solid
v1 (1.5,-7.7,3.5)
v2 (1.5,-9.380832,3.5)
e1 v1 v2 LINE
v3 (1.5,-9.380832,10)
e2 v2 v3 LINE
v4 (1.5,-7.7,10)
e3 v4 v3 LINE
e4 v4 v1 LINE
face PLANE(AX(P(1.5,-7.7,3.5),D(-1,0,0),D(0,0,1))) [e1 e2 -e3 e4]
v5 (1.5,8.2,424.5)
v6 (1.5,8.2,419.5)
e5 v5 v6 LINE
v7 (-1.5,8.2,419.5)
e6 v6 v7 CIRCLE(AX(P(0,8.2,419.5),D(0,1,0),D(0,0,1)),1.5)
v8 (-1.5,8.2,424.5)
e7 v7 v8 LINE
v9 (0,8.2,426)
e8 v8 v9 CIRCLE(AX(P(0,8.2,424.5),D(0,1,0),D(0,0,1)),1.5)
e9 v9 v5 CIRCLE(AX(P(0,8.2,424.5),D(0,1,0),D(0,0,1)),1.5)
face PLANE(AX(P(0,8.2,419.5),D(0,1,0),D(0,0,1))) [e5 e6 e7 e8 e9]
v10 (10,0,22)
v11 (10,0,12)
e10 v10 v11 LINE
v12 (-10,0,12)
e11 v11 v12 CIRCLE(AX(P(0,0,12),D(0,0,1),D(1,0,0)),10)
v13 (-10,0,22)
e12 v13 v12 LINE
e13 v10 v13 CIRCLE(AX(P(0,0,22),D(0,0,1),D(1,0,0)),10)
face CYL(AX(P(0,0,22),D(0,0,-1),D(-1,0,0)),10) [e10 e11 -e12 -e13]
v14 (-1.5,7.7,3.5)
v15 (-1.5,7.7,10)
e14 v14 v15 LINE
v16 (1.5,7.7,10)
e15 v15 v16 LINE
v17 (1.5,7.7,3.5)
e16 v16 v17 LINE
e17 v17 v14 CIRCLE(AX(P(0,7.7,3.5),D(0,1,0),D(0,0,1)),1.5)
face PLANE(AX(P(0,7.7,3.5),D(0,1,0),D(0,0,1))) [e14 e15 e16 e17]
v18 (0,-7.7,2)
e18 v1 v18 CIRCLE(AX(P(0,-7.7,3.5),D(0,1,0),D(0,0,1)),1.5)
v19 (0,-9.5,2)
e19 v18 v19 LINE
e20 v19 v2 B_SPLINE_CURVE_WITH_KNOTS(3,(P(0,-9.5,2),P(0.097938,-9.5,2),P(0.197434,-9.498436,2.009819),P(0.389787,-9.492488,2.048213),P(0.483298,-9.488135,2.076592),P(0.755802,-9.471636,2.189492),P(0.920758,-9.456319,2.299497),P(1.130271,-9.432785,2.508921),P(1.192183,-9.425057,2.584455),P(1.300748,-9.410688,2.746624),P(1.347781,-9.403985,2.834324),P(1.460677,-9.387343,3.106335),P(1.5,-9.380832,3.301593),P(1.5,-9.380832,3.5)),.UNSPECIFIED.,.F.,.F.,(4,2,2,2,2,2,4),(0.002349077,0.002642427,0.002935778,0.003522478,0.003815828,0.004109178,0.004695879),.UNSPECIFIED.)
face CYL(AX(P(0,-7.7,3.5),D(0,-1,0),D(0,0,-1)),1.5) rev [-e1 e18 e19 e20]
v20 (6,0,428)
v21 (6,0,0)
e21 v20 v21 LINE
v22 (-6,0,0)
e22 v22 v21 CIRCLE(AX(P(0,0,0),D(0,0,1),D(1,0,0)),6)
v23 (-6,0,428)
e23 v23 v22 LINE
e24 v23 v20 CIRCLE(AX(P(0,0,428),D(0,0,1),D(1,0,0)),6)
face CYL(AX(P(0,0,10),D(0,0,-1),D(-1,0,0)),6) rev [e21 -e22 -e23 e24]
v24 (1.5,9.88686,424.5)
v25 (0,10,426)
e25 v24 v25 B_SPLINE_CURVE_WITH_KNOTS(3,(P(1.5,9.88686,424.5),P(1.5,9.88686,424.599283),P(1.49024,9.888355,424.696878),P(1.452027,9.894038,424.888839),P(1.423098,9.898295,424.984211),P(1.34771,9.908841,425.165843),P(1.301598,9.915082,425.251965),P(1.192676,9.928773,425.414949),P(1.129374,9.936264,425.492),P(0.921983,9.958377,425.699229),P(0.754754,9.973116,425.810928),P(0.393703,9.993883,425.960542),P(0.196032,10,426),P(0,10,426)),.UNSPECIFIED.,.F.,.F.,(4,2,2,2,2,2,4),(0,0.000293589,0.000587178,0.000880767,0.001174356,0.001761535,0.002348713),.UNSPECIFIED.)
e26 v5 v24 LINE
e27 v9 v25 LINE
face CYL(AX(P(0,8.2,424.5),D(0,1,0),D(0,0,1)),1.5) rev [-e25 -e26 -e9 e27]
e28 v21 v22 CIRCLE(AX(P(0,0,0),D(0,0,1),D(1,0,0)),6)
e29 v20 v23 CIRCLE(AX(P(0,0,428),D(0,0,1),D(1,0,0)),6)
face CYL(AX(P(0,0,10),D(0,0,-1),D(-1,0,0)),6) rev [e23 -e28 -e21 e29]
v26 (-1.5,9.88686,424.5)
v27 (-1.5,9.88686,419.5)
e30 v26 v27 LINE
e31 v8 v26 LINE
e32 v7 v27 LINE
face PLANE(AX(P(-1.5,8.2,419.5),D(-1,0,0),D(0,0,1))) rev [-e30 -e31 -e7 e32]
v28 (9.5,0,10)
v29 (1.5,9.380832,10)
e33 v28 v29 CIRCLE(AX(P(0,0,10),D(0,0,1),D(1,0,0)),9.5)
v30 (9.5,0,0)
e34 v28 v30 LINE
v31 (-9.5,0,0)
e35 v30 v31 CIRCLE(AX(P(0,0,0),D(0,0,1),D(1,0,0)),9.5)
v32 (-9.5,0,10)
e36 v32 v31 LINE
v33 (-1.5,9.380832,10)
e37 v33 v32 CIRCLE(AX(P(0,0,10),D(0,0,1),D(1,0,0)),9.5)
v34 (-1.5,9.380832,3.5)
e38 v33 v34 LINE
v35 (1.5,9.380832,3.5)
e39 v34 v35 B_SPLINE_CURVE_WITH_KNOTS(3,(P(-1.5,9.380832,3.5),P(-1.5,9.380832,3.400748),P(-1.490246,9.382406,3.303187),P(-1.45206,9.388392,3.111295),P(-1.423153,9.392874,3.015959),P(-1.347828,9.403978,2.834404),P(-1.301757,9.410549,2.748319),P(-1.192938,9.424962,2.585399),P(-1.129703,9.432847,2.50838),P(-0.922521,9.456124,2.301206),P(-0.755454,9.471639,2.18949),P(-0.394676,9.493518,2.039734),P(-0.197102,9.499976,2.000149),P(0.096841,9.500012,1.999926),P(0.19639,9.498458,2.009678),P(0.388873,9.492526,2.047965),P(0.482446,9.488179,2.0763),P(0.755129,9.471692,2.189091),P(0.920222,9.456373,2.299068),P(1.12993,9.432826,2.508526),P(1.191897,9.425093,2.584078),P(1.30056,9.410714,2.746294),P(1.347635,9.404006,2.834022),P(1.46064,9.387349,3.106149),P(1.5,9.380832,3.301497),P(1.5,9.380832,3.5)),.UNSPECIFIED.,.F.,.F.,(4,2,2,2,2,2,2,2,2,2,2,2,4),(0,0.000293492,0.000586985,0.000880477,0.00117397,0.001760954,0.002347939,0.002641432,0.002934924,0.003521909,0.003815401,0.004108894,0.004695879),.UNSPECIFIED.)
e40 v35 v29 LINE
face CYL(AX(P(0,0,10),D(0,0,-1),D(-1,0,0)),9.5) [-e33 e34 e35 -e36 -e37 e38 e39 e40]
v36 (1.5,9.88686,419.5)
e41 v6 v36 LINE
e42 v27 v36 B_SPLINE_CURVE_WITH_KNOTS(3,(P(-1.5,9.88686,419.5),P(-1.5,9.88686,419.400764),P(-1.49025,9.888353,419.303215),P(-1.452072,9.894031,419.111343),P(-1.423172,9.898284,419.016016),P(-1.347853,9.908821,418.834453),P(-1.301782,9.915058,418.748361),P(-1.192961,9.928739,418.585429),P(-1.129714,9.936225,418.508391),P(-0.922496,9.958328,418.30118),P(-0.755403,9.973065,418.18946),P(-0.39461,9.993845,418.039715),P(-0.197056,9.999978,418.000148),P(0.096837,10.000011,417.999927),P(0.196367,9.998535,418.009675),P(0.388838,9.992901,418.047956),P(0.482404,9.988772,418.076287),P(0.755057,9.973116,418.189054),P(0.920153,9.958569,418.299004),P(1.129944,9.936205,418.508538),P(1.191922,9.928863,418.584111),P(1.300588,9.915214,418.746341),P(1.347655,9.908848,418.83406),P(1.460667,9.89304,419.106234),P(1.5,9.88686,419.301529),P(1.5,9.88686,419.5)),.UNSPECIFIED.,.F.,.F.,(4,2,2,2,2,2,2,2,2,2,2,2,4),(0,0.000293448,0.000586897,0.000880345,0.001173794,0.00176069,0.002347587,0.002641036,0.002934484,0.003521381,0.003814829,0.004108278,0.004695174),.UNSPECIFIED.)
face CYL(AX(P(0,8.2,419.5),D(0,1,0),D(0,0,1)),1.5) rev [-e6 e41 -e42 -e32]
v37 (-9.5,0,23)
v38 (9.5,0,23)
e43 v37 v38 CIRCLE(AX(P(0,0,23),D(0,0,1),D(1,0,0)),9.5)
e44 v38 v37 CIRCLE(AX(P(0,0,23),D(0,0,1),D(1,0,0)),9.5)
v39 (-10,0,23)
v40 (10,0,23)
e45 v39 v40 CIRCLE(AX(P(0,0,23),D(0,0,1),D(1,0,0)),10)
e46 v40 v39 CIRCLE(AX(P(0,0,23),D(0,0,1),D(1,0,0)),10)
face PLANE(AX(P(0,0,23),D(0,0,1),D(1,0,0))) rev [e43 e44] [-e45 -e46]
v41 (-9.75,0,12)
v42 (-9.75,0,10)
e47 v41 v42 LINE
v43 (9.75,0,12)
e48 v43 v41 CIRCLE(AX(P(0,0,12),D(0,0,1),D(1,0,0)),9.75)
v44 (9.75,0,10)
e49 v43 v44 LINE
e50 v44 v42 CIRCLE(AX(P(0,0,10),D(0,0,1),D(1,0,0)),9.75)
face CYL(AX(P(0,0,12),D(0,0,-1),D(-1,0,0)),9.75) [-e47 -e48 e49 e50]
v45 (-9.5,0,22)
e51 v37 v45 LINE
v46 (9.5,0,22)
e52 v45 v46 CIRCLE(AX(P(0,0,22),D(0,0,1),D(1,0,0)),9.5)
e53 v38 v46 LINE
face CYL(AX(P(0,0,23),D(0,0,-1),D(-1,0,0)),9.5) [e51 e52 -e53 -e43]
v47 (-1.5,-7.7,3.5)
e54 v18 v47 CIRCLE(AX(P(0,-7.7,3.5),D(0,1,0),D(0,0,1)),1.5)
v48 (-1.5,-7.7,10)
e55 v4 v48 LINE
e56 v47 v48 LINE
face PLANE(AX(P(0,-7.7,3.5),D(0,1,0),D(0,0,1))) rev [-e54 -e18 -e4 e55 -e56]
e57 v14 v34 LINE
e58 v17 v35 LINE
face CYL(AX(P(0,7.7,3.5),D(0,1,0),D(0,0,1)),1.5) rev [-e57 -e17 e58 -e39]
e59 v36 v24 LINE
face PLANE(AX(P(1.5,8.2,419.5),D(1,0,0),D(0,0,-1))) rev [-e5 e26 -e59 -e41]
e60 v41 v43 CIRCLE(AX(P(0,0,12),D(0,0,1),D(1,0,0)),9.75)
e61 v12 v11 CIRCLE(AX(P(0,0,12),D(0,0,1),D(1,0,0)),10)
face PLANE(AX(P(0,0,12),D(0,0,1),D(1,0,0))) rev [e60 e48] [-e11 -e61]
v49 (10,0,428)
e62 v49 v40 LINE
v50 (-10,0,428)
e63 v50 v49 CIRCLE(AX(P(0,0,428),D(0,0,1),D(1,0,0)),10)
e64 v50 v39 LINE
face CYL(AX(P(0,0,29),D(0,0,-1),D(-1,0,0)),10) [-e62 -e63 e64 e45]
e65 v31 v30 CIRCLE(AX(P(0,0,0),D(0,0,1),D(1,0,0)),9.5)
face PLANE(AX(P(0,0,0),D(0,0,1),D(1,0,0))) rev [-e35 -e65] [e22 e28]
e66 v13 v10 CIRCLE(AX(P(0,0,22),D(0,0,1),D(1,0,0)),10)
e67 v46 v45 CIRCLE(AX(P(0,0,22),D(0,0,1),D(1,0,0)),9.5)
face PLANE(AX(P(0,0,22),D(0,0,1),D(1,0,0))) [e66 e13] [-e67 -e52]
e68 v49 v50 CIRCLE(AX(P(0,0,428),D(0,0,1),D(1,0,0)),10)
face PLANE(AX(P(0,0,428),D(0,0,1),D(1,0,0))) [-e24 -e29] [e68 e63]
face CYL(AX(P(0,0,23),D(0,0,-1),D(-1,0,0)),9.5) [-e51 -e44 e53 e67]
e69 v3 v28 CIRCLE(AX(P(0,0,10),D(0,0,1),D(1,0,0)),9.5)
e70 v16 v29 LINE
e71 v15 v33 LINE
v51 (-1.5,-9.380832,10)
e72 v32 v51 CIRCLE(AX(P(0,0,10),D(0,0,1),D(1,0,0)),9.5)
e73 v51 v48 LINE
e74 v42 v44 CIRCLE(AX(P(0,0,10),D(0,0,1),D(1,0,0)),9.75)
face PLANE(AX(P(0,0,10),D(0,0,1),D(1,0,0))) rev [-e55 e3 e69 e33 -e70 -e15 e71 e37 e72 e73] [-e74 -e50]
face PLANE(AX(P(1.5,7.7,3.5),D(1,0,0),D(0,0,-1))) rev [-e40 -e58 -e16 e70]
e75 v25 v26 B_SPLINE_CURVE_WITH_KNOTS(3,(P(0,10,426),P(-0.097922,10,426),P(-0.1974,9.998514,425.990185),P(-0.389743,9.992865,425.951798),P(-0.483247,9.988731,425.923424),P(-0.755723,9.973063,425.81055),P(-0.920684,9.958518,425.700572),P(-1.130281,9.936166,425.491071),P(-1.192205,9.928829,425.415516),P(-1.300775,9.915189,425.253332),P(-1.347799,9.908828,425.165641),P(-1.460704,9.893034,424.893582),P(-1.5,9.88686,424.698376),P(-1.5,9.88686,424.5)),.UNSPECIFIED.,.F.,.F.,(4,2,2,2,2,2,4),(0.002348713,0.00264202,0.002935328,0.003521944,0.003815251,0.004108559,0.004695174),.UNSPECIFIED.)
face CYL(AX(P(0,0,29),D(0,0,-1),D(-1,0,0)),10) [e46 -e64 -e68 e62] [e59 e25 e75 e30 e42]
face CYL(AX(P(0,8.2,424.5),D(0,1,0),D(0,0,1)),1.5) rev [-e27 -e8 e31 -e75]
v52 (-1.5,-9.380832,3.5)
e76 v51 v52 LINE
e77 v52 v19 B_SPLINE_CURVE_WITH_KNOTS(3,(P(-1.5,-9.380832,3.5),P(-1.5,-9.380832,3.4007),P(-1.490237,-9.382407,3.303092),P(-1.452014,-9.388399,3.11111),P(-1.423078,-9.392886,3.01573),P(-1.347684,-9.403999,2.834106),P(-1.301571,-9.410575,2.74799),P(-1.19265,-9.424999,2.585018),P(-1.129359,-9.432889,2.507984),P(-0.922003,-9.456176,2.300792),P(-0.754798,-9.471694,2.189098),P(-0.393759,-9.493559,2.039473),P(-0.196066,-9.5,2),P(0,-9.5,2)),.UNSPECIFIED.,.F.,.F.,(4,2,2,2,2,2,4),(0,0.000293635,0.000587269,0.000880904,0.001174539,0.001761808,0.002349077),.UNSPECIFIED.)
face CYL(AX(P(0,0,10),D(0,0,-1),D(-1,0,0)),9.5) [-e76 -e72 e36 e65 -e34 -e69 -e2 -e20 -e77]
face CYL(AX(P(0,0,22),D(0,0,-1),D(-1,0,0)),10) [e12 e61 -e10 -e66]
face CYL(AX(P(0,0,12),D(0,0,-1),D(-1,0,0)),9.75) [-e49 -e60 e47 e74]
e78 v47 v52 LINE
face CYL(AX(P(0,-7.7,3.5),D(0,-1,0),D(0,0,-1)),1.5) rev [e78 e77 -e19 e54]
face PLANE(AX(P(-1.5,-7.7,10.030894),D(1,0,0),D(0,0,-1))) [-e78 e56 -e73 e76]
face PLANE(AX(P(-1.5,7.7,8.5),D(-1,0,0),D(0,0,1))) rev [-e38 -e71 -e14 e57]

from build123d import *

# Parameters (mm, degrees)
SKETCH1_R           = 9.5
SKETCH1_R_2         = 6
BOSS_EXTRUDE1_DEPTH = 10
CUT_EXTRUDE1_DEPTH  = 1.8
CUT_EXTRUDE2_START  = 1.8
CUT_EXTRUDE2_DEPTH  = 1.8
SKETCH4_R           = 9.75
SKETCH4_R_2         = 6
BOSS_EXTRUDE2_DEPTH = 2
SKETCH5_R           = 10
BOSS_EXTRUDE3_DEPTH = 10
SKETCH6_R           = 6
CUT_EXTRUDE3_DEPTH  = 27.153393745
SKETCH7_R           = 9.5
SKETCH7_R_2         = 6
BOSS_EXTRUDE4_DEPTH = 1
SKETCH8_R           = 10
SKETCH8_R_2         = 6
BOSS_EXTRUDE5_DEPTH = 6
SKETCH9_R           = 10
SKETCH9_R_2         = 6
BOSS_EXTRUDE6_DEPTH = 150
SKETCH10_R          = 10
SKETCH10_R_2        = 6
BOSS_EXTRUDE7_DEPTH = 223
SKETCH11_R          = 10
SKETCH11_R_2        = 6
BOSS_EXTRUDE8_DEPTH = 26
CUT_EXTRUDE4_DEPTH  = 1.8


with BuildPart() as part:
    # Sketch1 → Boss-Extrude1 (new body)
    with BuildSketch(Plane.XY):
        Circle(SKETCH1_R)
        Circle(SKETCH1_R_2, mode=Mode.SUBTRACT)
    extrude(amount=BOSS_EXTRUDE1_DEPTH)

    # Sketch2 → Cut-Extrude1 (cut)
    with BuildSketch(Plane(origin=(0, 9.5, 0), x_dir=(1, 0, 0), z_dir=(0, 1, 0))):
        with BuildLine():
            Line((1.5, -3.5), (1.5, -8.5))
            Line((1.5, -8.5), (1.5, -10))
            Line((1.5, -10), (-1.5, -10))
            Line((-1.5, -10), (-1.5, -8.5))
            Line((-1.5, -8.5), (-1.5, -3.5))
            ThreePointArc((-1.5, -3.5), (0, -2), (1.5, -3.5))
        make_face()
    extrude(amount=-CUT_EXTRUDE1_DEPTH, mode=Mode.SUBTRACT)

    # Sketch3 → Cut-Extrude2 (cut)
    with BuildSketch(Plane(origin=(0, -9.5, 0), x_dir=(1, 0, 0), z_dir=(0, 1, 0)).offset(CUT_EXTRUDE2_START)):
        with BuildLine():
            Line((1.5, -3.5), (1.5, -8.5))
            Line((1.5, -8.5), (1.5, -10.030894453))
            Line((1.5, -10.030894453), (-1.5, -10.030894453))
            Line((-1.5, -10.030894453), (-1.5, -8.5))
            Line((-1.5, -8.5), (-1.5, -3.5))
            ThreePointArc((-1.5, -3.5), (0, -2), (1.5, -3.5))
        make_face()
    extrude(amount=-CUT_EXTRUDE2_DEPTH, mode=Mode.SUBTRACT)

    # Sketch4 → Boss-Extrude2 (add)
    with BuildSketch(Plane.XY.offset(10)):
        Circle(SKETCH4_R)
        Circle(SKETCH4_R_2, mode=Mode.SUBTRACT)
    extrude(amount=BOSS_EXTRUDE2_DEPTH)

    # Sketch5 → Boss-Extrude3 (add)
    with BuildSketch(Plane.XY.offset(12)):
        Circle(SKETCH5_R)
    extrude(amount=BOSS_EXTRUDE3_DEPTH)

    # Sketch6 → Cut-Extrude3 (cut, through all)
    with BuildSketch(Plane.XY.offset(22)):
        Circle(SKETCH6_R)
    extrude(amount=-CUT_EXTRUDE3_DEPTH, mode=Mode.SUBTRACT)

    # Sketch7 → Boss-Extrude4 (add)
    with BuildSketch(Plane.XY.offset(22)):
        with Locations(Location((0, 0, 0), (0, 0, 260.915279713))):
            Circle(SKETCH7_R)
        Circle(SKETCH7_R_2, mode=Mode.SUBTRACT)
    extrude(amount=BOSS_EXTRUDE4_DEPTH)

    # Sketch8 → Boss-Extrude5 (add)
    with BuildSketch(Plane.XY.offset(23)):
        Circle(SKETCH8_R)
        Circle(SKETCH8_R_2, mode=Mode.SUBTRACT)
    extrude(amount=BOSS_EXTRUDE5_DEPTH)

    # Sketch9 → Boss-Extrude6 (add)
    with BuildSketch(Plane.XY.offset(29)):
        Circle(SKETCH9_R)
        Circle(SKETCH9_R_2, mode=Mode.SUBTRACT)
    extrude(amount=BOSS_EXTRUDE6_DEPTH)

    # Sketch10 → Boss-Extrude7 (add)
    with BuildSketch(Plane.XY.offset(179)):
        Circle(SKETCH10_R)
        Circle(SKETCH10_R_2, mode=Mode.SUBTRACT)
    extrude(amount=BOSS_EXTRUDE7_DEPTH)

    # Sketch11 → Boss-Extrude8 (add)
    with BuildSketch(Plane.XY.offset(402)):
        Circle(SKETCH11_R)
        Circle(SKETCH11_R_2, mode=Mode.SUBTRACT)
    extrude(amount=BOSS_EXTRUDE8_DEPTH)

    # Sketch12 → Cut-Extrude4 (cut)
    with BuildSketch(Plane(origin=(0, 10, 0), x_dir=(1, 0, 0), z_dir=(0, 1, 0))):
        with BuildLine():
            Line((1.5, -419.5), (1.5, -424.5))
            ThreePointArc((1.5, -424.5), (0, -426), (-1.5, -424.5))
            Line((-1.5, -424.5), (-1.5, -419.5))
            ThreePointArc((-1.5, -419.5), (0, -418), (1.5, -419.5))
        make_face()
    extrude(amount=-CUT_EXTRUDE4_DEPTH, mode=Mode.SUBTRACT)


solid = part.part
